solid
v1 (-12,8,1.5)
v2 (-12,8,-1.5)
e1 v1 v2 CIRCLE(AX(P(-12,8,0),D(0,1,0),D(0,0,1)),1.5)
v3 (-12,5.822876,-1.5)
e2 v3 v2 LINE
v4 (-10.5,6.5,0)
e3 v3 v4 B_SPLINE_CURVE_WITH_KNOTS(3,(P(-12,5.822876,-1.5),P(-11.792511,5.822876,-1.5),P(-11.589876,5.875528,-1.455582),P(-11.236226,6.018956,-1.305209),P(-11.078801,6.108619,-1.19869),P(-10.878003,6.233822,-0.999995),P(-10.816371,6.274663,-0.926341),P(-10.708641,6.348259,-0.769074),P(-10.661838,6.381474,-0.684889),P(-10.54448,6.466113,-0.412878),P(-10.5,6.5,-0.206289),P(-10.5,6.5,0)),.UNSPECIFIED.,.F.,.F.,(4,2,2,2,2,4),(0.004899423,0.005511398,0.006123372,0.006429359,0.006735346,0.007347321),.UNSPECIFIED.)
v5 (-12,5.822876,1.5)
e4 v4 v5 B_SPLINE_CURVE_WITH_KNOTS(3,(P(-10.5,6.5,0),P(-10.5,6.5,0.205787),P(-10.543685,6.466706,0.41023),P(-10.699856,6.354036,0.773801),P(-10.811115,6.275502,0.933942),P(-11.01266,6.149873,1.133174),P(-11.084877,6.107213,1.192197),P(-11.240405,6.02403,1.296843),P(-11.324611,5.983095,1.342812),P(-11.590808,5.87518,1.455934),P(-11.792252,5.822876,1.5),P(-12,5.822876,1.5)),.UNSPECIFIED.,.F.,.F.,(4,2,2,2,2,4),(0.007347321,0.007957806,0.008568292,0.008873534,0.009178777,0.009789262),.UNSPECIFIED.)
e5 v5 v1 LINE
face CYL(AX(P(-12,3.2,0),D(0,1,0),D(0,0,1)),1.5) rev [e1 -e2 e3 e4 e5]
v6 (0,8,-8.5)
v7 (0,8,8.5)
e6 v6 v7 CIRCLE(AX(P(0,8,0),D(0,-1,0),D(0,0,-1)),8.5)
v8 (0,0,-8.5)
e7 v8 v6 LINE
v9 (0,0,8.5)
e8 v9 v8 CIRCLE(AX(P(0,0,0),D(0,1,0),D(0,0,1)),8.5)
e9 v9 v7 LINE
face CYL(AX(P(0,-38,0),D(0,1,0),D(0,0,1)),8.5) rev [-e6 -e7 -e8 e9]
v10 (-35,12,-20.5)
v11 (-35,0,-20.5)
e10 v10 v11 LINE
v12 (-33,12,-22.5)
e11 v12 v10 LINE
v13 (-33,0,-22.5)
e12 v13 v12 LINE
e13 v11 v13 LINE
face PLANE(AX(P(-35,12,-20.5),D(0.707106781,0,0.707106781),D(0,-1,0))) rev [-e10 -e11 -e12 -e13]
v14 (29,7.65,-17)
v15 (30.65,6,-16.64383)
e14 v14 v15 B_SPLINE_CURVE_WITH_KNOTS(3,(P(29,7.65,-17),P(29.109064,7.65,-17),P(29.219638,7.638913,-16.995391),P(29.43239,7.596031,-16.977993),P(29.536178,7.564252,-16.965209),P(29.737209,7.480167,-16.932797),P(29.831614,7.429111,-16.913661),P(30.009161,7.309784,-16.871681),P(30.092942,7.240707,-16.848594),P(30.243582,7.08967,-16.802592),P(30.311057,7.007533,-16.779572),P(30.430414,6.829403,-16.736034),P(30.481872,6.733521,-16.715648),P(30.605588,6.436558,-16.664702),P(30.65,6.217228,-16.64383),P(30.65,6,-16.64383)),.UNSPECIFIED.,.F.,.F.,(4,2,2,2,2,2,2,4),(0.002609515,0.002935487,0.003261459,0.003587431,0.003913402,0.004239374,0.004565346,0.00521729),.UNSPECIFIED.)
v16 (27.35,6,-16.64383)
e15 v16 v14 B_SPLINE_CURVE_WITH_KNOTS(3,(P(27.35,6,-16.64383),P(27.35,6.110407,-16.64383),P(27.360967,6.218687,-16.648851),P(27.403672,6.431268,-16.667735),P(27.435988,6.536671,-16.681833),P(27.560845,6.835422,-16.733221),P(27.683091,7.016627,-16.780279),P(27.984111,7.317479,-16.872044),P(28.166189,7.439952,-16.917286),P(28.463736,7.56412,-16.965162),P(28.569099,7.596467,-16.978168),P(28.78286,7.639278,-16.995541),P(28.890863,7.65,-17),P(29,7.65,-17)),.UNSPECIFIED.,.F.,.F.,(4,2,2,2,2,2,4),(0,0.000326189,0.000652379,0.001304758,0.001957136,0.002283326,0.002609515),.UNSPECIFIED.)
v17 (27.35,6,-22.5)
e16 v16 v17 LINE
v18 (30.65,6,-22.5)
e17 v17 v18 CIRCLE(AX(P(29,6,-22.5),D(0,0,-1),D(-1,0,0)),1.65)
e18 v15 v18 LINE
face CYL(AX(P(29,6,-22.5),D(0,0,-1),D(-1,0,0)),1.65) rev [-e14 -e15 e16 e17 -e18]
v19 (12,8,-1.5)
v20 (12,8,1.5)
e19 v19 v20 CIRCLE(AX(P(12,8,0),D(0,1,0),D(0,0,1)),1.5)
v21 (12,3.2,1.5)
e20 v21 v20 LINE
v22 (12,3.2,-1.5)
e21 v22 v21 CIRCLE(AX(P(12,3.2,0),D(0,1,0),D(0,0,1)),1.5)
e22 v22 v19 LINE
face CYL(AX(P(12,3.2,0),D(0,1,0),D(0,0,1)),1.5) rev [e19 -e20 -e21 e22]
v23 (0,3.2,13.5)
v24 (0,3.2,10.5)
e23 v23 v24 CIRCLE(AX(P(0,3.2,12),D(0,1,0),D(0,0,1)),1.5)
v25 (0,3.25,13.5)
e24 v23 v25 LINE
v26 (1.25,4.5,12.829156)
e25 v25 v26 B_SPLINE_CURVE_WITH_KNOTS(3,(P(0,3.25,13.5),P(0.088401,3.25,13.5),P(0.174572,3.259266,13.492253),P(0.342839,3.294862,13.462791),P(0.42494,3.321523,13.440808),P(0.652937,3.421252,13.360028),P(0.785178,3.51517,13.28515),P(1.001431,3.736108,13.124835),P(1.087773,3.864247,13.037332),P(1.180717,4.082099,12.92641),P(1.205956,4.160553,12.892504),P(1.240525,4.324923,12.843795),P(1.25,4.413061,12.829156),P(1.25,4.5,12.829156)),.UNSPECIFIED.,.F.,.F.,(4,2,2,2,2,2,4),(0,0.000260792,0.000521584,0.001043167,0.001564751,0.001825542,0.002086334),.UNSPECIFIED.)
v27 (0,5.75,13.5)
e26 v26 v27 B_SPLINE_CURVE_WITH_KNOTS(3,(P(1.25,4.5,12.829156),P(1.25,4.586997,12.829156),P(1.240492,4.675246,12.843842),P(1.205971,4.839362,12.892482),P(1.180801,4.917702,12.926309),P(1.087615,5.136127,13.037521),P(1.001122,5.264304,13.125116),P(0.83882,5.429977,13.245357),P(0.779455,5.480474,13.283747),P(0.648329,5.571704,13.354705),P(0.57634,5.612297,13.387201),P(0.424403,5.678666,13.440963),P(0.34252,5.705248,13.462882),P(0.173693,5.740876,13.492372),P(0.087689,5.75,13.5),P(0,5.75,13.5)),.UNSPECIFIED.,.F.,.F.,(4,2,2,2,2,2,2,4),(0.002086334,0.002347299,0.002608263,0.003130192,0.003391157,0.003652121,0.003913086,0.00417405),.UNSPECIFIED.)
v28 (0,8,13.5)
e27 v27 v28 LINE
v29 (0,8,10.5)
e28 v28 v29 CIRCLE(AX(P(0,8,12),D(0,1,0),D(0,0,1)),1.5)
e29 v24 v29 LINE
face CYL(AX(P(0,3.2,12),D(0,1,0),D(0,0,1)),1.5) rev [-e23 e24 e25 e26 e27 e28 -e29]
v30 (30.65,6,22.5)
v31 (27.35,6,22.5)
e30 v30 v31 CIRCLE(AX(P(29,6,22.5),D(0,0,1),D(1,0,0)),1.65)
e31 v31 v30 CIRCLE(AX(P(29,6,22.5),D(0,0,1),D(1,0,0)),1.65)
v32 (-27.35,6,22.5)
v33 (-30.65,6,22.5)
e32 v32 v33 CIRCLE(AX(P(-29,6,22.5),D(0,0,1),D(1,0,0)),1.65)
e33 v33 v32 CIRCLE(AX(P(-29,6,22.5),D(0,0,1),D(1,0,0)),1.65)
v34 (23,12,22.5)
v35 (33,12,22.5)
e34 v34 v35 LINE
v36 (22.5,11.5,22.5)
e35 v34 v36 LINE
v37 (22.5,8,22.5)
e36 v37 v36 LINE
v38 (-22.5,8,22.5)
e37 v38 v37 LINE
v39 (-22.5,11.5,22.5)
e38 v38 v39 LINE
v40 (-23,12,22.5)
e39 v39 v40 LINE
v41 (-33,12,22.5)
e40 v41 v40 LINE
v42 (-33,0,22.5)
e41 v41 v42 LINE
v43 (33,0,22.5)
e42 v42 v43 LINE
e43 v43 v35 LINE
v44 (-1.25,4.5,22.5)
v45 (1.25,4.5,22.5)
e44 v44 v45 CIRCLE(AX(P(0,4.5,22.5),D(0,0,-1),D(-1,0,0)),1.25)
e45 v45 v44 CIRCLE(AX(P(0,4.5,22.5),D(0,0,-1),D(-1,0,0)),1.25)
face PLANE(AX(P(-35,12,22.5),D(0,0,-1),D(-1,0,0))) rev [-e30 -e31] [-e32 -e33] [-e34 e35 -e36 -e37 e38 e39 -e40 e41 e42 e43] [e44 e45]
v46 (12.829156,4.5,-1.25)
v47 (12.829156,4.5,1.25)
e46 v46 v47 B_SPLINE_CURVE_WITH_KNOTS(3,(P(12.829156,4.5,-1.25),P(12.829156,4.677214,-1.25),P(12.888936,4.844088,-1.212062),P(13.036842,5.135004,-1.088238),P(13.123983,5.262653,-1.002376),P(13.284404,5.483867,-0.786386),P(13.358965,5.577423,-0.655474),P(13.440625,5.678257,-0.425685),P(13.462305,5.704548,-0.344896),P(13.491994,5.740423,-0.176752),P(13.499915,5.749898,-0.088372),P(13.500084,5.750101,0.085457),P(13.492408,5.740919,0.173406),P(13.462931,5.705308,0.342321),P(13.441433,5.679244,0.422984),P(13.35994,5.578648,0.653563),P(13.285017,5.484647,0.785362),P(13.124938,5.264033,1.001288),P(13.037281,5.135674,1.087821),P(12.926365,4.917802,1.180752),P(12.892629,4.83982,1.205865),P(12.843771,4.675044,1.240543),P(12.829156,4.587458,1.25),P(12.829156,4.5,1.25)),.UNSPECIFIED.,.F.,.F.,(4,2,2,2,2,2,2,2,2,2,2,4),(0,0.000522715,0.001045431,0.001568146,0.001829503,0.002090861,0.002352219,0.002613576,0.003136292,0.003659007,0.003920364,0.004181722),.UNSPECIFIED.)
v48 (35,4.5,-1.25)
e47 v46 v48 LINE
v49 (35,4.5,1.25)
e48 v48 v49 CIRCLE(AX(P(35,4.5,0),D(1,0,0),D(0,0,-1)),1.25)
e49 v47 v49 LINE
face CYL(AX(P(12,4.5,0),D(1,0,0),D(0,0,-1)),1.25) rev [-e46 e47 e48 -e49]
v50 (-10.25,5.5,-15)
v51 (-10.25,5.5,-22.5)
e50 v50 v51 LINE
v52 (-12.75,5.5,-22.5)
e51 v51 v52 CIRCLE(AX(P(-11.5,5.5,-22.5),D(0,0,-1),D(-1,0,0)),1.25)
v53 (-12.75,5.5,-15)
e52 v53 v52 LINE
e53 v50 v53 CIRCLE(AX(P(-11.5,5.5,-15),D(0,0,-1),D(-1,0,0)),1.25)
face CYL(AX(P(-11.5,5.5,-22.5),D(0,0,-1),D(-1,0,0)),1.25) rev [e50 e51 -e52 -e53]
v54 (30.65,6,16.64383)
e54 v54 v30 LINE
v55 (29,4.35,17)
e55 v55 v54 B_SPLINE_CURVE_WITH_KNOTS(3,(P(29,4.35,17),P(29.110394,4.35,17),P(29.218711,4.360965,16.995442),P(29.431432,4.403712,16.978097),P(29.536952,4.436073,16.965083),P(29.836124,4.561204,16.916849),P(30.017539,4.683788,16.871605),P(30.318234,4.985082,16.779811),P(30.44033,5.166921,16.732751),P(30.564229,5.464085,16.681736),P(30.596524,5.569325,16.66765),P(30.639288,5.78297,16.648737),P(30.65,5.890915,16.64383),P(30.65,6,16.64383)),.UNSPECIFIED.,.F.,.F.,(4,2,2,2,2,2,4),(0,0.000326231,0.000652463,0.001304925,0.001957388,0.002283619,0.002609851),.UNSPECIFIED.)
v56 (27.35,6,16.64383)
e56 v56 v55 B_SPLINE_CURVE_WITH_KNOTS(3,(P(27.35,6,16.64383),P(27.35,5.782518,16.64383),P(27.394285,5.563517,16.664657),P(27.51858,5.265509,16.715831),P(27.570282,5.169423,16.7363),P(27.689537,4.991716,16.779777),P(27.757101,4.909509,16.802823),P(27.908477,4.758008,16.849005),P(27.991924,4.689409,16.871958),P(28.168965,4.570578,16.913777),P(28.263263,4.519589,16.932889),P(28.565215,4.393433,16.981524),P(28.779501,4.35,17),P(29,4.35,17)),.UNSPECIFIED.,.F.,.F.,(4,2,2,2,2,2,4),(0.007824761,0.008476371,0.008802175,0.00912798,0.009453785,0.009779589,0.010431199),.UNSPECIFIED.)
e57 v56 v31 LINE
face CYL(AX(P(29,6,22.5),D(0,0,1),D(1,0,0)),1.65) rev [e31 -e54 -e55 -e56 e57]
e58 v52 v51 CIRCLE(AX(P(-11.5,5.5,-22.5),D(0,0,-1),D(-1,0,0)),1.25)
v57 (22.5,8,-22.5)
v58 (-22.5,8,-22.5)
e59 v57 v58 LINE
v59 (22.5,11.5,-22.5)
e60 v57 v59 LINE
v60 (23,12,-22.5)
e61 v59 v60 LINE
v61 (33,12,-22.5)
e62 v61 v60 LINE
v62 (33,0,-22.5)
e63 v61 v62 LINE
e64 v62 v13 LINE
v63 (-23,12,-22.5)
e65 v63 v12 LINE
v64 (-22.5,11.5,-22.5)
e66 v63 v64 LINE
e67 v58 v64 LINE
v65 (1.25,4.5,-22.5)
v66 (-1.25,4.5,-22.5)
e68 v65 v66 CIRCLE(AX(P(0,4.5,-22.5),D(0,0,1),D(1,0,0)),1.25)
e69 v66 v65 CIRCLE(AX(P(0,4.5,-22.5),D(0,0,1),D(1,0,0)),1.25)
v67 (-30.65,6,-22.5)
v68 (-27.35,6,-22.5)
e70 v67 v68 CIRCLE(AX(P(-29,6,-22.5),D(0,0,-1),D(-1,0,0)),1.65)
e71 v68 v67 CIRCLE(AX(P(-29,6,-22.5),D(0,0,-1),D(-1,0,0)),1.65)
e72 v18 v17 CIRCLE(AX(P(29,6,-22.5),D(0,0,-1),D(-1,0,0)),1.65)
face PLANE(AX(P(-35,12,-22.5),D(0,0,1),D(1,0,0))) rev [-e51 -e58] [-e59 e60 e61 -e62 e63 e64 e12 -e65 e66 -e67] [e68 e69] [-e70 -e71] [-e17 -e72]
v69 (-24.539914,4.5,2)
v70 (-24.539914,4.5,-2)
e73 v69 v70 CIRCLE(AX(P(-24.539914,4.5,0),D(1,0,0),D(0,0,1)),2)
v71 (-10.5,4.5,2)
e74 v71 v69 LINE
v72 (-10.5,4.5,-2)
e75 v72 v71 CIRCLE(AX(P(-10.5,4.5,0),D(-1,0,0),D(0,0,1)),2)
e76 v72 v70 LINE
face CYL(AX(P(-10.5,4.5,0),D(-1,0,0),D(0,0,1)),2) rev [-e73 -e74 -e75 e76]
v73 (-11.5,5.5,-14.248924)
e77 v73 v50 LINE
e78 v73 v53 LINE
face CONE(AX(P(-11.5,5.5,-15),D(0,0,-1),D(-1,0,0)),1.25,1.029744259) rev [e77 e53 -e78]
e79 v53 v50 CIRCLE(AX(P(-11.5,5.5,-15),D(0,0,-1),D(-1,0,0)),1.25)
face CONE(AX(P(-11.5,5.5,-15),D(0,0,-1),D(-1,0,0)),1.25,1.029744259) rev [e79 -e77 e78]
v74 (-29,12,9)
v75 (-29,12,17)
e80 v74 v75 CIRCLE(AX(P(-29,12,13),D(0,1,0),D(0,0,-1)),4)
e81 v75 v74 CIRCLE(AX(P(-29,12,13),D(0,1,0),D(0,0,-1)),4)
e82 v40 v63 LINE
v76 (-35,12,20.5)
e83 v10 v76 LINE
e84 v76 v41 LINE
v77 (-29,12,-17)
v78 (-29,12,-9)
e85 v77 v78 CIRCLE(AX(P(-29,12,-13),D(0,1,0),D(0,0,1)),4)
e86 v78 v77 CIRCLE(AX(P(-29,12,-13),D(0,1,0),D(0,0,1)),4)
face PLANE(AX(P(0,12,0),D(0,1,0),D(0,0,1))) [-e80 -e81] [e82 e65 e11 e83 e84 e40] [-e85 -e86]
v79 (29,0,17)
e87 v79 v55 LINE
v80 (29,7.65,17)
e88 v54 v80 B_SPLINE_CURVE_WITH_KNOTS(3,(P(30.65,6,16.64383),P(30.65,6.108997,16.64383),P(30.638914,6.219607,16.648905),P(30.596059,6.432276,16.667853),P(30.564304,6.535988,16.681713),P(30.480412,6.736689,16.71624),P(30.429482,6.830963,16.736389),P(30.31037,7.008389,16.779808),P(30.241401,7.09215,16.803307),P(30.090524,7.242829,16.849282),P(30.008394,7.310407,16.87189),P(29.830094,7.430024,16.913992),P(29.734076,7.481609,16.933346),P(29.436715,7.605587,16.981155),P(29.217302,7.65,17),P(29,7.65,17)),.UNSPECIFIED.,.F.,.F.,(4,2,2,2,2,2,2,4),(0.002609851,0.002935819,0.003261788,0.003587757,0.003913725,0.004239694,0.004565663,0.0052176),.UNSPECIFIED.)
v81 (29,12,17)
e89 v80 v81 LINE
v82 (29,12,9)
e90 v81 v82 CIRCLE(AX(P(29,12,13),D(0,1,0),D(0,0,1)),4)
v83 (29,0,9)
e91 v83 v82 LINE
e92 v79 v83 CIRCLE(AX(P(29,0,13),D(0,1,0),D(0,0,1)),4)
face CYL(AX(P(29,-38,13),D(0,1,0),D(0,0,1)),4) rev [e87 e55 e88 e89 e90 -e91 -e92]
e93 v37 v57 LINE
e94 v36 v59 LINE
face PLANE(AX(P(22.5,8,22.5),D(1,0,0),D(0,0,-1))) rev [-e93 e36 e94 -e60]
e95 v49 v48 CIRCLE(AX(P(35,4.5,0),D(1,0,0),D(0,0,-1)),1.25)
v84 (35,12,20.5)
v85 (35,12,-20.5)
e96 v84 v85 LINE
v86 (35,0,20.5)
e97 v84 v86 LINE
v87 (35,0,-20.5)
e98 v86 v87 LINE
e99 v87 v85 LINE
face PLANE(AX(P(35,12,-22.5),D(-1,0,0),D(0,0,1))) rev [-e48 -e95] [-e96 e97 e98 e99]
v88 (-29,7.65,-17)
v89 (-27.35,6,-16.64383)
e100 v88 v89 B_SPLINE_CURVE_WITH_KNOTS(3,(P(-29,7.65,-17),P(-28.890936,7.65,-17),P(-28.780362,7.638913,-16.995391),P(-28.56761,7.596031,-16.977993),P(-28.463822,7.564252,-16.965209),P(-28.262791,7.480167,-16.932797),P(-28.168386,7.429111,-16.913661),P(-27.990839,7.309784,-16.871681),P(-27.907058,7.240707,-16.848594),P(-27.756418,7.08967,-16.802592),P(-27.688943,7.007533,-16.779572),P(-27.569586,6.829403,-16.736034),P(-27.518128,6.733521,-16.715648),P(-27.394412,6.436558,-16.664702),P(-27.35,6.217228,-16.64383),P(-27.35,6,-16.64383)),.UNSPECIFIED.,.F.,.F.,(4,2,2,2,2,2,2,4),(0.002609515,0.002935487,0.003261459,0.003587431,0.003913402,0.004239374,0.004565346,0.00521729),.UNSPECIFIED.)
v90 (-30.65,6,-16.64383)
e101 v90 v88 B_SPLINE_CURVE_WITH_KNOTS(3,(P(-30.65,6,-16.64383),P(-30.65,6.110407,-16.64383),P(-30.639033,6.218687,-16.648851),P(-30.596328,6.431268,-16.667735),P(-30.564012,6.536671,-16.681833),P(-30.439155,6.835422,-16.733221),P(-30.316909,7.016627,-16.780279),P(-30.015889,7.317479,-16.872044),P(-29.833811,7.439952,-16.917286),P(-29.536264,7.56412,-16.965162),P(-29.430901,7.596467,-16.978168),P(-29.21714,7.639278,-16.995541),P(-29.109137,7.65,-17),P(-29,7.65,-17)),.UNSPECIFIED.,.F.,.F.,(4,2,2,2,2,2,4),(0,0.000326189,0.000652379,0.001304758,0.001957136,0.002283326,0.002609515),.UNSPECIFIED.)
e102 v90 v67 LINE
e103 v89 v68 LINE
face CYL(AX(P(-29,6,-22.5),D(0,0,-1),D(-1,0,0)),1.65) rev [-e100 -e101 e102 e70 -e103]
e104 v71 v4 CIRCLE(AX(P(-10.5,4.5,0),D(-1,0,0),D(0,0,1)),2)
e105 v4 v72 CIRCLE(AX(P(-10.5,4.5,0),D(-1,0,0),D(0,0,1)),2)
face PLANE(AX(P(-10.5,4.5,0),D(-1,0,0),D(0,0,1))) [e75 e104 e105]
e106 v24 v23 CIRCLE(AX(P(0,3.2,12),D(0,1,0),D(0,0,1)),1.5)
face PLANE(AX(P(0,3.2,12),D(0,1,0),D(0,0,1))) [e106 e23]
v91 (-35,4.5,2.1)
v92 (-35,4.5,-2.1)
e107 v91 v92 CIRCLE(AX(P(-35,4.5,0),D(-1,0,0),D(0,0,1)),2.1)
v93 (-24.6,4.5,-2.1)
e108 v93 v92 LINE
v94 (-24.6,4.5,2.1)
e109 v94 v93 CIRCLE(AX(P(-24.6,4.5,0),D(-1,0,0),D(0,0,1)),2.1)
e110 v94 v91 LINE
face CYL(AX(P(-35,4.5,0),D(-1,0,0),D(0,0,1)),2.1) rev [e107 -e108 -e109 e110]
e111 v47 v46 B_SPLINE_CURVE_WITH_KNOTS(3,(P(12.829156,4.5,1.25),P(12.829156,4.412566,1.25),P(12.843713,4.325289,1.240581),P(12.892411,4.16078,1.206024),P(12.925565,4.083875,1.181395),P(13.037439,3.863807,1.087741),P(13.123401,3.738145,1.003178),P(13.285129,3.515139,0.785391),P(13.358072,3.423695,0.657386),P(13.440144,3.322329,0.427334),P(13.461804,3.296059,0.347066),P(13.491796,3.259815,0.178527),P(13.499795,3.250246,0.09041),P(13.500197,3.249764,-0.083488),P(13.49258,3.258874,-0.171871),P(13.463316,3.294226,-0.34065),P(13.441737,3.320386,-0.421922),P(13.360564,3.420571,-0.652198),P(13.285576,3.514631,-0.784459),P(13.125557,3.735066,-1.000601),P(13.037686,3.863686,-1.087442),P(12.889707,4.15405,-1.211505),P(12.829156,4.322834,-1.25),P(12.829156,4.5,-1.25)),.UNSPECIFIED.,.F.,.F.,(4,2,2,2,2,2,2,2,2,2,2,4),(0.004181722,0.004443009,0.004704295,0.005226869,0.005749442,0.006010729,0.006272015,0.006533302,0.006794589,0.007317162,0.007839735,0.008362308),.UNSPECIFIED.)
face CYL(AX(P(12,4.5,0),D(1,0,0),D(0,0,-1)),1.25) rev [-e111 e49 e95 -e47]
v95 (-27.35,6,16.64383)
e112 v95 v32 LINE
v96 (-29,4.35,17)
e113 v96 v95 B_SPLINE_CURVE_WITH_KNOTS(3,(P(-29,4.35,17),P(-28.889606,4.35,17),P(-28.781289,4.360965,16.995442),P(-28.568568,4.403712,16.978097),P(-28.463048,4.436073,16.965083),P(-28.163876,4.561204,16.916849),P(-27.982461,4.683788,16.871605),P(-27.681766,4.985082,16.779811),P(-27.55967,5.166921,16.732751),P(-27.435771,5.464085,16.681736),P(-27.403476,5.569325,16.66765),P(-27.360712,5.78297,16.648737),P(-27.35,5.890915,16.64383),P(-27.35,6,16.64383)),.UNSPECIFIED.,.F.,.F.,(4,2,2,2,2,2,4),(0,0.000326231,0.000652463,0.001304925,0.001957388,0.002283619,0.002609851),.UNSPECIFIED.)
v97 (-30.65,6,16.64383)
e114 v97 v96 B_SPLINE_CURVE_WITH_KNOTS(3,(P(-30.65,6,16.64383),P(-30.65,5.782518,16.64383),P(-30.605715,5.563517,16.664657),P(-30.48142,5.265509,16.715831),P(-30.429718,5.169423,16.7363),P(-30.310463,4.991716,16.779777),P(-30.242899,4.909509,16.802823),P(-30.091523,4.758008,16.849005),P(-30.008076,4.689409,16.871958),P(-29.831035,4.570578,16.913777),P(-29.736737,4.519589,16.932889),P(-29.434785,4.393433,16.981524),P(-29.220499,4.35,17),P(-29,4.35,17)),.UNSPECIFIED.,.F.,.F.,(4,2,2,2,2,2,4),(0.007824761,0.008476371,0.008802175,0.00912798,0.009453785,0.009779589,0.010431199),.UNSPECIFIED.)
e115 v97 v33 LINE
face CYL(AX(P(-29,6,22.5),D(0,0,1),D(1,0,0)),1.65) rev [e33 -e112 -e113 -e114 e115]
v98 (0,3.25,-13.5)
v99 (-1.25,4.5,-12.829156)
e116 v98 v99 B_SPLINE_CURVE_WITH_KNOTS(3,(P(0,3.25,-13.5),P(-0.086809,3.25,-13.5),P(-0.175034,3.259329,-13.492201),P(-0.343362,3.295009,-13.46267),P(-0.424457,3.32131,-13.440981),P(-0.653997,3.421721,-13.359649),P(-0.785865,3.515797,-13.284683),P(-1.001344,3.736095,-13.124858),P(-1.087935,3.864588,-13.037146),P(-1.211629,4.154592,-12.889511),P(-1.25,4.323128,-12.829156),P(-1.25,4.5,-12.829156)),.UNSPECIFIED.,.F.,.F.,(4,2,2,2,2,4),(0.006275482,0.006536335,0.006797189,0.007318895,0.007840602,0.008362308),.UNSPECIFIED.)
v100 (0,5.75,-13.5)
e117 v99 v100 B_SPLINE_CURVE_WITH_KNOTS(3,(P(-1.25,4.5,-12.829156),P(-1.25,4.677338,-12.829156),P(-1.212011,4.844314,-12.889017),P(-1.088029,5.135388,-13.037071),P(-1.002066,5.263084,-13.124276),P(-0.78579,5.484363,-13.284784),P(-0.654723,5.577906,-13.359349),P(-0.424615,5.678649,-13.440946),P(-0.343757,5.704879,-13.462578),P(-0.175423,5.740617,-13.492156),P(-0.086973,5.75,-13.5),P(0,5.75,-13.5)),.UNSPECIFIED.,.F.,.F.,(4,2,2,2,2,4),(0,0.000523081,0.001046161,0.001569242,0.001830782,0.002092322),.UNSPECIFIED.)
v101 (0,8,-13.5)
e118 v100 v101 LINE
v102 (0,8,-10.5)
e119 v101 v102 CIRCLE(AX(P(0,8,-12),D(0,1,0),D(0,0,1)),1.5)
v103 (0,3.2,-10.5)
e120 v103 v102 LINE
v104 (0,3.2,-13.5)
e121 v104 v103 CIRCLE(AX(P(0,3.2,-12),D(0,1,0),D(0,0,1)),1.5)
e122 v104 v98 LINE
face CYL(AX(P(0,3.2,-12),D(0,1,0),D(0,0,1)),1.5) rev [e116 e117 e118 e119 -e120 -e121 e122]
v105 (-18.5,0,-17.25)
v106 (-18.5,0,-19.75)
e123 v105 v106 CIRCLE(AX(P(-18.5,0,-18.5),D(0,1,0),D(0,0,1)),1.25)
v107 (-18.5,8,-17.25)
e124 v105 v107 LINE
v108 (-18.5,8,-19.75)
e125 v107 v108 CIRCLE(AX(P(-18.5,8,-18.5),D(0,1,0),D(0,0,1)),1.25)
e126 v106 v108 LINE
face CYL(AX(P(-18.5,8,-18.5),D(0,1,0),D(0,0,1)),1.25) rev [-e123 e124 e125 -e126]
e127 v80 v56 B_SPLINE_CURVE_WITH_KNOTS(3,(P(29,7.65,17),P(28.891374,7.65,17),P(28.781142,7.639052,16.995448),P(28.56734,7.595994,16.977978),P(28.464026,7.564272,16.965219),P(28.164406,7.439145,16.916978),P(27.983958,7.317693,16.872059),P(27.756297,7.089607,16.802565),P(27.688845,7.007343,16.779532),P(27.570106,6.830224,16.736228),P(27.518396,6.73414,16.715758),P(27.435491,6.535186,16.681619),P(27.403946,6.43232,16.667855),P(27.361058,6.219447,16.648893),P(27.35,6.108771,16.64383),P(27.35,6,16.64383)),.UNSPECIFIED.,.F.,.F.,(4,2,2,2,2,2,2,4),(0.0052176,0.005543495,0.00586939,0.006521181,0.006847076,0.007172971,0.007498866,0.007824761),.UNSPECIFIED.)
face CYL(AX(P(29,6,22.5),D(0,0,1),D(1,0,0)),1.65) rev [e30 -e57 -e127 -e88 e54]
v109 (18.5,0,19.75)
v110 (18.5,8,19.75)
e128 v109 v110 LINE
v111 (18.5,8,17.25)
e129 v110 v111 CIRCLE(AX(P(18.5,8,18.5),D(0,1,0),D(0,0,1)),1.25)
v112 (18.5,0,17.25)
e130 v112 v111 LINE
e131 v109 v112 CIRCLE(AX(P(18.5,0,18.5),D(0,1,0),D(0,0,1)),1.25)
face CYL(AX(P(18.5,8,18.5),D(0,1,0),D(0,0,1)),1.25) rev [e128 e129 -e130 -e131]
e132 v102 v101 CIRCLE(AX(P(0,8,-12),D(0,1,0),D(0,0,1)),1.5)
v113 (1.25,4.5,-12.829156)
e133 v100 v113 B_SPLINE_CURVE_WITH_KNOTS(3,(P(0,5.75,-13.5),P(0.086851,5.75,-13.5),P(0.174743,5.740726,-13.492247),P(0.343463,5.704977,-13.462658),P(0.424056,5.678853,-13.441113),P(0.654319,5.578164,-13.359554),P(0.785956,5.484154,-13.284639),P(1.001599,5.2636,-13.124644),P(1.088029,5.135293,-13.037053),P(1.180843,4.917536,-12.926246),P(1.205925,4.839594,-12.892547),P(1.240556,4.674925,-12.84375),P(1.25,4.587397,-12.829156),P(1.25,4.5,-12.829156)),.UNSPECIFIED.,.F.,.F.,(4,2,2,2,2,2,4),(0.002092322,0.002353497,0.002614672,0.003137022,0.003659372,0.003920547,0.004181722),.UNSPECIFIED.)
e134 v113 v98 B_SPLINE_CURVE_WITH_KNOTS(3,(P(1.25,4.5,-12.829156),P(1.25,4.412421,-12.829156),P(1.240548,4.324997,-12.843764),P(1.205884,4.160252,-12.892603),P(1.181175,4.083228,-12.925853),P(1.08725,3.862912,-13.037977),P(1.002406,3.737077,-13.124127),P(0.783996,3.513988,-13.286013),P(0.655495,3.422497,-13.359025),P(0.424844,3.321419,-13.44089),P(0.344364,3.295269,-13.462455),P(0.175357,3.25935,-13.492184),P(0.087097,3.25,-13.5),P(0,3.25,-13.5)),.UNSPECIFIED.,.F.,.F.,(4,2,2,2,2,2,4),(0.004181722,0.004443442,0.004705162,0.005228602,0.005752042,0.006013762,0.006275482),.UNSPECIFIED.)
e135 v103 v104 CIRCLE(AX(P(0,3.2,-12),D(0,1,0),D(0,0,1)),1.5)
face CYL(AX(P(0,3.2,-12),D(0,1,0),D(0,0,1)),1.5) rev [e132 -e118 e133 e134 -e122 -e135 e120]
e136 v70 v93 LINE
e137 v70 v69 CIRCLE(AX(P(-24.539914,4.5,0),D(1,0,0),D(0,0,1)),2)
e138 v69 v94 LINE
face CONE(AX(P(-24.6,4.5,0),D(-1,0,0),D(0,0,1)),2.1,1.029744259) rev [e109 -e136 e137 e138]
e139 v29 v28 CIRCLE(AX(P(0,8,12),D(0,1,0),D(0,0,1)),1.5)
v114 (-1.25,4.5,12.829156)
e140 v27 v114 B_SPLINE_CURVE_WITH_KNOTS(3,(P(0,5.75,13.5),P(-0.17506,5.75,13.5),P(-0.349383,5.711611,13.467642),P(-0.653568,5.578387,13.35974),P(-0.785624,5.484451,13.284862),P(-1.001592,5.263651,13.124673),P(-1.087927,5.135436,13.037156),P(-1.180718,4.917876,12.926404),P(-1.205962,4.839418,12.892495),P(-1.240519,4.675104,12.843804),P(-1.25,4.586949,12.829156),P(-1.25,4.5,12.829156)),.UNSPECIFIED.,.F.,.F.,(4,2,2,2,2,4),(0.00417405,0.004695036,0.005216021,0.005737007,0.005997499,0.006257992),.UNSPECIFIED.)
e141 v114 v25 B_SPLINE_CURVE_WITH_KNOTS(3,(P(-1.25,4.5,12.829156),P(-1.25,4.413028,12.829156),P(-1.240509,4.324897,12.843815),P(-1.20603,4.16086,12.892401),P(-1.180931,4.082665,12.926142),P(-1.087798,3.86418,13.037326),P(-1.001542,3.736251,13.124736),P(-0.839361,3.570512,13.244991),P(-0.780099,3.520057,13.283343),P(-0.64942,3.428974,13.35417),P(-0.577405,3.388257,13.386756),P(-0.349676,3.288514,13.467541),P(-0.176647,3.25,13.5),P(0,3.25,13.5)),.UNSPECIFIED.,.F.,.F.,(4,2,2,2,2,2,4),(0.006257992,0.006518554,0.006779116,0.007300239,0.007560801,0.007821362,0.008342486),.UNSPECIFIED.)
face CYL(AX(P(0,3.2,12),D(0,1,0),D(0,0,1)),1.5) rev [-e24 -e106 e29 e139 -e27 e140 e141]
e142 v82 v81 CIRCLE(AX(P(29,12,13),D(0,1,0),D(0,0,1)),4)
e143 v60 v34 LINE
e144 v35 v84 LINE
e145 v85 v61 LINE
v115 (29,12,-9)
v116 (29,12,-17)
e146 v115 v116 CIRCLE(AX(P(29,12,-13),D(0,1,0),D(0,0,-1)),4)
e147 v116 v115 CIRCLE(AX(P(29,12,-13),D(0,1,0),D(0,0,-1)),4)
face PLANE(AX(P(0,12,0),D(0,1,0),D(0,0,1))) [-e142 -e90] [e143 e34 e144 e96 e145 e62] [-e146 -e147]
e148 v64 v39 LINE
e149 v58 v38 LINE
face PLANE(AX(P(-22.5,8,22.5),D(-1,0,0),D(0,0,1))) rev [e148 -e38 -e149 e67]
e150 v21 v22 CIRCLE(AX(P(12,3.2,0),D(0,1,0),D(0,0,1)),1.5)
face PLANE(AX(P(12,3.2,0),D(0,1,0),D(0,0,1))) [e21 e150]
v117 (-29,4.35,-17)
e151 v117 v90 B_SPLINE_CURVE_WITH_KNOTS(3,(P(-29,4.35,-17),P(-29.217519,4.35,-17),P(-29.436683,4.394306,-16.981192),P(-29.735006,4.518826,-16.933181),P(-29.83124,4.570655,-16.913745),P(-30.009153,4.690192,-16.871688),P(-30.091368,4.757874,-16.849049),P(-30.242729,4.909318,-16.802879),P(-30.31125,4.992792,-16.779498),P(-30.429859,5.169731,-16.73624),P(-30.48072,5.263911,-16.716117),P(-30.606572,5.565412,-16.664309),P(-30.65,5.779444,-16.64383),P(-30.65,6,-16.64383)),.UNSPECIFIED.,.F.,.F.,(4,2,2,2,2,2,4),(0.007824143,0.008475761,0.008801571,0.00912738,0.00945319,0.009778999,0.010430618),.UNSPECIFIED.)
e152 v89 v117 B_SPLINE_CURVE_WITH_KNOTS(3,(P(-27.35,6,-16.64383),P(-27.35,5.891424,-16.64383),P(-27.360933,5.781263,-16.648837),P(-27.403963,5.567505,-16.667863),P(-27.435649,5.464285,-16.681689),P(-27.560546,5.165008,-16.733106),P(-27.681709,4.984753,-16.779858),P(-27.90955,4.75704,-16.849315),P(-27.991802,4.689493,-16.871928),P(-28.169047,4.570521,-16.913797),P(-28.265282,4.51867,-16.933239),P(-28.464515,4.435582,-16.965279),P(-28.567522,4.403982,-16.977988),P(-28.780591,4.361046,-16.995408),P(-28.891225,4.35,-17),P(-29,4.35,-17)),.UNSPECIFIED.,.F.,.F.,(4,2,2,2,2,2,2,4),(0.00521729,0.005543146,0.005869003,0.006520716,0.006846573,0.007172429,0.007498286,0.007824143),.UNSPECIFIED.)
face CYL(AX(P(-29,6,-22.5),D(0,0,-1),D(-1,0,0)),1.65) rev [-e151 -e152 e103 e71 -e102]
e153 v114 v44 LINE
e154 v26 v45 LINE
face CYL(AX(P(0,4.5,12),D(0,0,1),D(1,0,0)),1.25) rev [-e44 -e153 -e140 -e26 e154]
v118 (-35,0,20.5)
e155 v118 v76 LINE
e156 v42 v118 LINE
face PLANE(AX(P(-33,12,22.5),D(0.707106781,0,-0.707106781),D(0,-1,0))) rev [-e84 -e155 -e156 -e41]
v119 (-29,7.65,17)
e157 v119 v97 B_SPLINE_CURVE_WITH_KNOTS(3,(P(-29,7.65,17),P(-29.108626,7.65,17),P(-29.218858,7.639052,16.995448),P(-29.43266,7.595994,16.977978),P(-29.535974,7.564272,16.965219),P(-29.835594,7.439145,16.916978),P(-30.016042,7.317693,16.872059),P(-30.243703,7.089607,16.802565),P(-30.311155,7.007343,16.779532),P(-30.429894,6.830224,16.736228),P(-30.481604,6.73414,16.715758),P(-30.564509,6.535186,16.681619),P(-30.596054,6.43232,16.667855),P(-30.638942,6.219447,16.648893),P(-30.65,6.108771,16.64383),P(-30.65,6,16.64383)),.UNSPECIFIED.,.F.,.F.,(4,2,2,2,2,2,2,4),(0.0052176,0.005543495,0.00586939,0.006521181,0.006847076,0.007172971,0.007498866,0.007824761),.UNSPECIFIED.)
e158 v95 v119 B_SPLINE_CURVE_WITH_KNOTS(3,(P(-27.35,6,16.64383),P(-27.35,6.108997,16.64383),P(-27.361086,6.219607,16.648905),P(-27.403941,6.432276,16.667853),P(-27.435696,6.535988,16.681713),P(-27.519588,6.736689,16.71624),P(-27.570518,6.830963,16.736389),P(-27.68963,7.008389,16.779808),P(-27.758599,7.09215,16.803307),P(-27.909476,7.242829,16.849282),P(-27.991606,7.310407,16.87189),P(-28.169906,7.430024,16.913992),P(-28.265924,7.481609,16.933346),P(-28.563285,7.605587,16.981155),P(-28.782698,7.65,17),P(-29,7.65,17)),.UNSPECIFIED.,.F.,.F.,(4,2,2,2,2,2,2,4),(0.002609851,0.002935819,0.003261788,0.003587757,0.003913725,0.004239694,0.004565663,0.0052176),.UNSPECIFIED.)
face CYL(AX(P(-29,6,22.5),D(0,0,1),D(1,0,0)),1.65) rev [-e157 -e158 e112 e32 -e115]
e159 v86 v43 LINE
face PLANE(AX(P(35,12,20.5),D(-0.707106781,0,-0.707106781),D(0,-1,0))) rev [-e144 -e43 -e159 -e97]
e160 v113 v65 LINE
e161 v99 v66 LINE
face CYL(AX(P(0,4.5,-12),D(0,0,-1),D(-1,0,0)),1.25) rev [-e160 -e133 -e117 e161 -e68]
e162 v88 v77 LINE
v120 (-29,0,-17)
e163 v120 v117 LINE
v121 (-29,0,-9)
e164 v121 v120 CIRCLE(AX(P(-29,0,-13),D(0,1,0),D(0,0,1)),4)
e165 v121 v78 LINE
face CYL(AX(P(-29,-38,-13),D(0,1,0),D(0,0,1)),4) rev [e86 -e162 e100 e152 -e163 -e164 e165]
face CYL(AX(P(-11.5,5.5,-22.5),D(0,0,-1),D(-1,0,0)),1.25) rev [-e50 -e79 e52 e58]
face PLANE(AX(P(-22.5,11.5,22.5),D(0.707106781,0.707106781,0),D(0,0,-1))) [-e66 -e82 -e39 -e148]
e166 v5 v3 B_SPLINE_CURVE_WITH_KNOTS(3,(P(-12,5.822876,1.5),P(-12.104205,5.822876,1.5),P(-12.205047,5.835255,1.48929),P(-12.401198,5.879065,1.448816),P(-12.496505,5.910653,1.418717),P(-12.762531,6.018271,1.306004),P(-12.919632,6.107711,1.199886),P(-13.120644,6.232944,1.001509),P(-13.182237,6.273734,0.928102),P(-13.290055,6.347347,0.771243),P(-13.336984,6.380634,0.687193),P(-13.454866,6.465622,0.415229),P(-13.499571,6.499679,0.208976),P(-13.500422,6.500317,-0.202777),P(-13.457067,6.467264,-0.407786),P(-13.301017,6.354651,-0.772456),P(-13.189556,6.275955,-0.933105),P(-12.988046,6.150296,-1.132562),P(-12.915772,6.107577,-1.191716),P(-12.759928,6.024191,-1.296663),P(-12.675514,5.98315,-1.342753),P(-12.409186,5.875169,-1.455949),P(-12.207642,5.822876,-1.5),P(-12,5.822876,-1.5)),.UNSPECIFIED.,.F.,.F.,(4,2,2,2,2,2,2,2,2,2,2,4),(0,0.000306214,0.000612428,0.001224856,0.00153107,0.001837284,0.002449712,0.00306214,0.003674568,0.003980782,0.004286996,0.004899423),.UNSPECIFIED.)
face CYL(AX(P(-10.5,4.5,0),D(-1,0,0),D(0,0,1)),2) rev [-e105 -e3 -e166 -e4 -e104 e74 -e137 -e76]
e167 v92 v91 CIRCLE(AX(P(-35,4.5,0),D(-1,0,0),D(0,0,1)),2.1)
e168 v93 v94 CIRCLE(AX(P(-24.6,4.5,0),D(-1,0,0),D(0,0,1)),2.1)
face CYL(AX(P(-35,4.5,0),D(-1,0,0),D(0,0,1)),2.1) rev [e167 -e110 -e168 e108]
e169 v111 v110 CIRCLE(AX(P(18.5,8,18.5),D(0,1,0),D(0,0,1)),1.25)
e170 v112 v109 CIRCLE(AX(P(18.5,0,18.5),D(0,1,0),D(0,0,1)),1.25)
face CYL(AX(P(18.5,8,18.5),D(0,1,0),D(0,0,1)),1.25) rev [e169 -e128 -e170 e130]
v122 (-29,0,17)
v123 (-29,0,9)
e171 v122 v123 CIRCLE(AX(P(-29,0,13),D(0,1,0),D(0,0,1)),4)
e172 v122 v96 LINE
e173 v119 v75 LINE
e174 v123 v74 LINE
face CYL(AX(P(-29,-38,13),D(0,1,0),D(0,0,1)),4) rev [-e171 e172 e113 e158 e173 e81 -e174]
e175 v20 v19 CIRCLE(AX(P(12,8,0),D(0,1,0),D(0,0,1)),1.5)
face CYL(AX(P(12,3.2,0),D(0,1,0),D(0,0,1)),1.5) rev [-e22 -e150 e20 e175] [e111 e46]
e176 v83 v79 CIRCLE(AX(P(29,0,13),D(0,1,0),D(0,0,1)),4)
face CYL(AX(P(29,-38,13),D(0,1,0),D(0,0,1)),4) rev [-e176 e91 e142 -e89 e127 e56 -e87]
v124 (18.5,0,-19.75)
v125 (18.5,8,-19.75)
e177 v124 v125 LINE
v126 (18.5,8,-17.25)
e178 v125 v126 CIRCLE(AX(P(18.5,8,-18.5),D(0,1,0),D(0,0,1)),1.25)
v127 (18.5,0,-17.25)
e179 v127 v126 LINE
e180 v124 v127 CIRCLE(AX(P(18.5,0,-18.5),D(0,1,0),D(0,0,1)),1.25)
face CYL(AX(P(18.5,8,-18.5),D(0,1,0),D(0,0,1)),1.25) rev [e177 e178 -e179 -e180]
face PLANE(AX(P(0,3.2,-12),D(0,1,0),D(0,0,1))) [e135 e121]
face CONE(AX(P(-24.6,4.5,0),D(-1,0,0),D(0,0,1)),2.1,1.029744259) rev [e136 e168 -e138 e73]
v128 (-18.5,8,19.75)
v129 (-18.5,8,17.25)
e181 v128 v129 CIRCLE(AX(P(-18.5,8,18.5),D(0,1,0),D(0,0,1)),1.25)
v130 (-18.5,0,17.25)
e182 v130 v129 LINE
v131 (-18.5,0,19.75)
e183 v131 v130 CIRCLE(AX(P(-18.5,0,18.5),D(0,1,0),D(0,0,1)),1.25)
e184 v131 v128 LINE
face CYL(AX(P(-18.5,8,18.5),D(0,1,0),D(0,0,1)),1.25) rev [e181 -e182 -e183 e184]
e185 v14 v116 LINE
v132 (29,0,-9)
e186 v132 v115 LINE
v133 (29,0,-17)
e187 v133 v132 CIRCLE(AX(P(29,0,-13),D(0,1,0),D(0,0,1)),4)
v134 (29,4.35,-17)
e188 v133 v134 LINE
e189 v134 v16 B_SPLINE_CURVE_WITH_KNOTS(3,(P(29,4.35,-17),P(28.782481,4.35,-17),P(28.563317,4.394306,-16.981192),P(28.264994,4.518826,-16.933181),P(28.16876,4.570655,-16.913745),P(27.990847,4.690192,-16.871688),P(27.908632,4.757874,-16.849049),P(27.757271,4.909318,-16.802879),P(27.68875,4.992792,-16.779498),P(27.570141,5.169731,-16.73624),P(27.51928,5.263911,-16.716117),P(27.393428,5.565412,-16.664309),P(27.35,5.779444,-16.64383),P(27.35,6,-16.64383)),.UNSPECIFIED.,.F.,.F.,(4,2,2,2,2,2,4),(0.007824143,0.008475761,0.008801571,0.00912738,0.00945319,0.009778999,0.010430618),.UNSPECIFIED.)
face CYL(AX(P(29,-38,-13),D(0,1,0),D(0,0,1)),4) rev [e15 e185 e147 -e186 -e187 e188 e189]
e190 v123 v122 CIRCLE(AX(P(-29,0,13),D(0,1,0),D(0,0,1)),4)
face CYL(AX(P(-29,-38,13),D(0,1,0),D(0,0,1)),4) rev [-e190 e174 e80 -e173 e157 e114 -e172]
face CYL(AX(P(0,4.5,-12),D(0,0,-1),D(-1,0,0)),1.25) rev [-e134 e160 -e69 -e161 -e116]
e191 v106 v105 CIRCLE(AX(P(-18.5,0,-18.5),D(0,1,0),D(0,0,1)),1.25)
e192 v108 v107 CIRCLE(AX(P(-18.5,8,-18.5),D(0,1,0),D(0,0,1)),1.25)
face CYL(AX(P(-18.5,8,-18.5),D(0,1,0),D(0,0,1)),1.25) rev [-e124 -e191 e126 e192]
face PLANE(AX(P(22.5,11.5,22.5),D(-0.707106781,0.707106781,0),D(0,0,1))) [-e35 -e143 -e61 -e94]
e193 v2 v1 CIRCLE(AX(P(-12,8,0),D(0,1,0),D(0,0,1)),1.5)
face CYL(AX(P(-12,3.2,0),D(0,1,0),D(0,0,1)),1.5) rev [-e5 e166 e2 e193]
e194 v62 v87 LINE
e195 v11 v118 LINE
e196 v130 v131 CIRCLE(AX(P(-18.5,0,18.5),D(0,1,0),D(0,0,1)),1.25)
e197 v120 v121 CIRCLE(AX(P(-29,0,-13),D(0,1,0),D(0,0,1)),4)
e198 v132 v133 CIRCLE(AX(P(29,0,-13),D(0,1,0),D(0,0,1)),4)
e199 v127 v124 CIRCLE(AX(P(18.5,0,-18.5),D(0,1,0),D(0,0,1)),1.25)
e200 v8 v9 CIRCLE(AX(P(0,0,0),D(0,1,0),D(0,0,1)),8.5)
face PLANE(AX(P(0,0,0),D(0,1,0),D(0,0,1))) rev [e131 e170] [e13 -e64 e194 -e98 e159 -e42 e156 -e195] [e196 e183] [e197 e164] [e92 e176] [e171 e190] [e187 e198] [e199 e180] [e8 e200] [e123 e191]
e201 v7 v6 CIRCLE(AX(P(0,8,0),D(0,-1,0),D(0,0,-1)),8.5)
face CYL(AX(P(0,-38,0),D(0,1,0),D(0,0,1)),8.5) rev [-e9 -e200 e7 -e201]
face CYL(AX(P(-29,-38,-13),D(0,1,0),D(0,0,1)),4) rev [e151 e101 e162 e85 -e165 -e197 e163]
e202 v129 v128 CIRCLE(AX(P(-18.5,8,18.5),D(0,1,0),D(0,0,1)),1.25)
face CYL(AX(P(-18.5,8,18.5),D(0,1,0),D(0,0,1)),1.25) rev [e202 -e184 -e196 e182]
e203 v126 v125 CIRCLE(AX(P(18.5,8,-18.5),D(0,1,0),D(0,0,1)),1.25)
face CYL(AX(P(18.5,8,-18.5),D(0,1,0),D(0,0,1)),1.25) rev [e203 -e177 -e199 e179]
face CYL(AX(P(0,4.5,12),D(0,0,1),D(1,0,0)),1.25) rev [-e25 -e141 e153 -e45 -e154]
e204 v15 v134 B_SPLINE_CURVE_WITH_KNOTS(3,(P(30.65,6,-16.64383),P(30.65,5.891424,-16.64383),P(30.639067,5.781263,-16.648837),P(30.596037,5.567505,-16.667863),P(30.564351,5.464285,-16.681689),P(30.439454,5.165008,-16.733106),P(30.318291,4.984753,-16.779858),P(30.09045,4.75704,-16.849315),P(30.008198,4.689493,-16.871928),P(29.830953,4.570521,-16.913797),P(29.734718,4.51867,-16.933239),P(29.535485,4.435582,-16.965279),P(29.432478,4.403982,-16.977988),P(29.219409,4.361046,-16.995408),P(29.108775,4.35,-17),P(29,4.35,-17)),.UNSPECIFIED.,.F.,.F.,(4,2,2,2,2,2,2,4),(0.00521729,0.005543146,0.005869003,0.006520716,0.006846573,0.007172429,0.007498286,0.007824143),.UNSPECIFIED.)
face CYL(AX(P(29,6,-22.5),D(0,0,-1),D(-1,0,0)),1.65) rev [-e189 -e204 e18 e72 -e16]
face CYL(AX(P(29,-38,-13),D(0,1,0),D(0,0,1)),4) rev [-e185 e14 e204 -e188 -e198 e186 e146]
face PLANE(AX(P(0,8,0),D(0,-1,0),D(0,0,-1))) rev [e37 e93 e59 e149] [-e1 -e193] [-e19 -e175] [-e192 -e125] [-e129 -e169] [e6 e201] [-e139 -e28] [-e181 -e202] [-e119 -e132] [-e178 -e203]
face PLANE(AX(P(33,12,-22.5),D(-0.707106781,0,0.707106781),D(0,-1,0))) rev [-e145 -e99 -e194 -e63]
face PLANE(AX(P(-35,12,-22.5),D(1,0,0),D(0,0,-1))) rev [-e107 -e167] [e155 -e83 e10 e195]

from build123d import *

# Parameters (mm, degrees)
SKETCH1_W                       = 70
SKETCH1_H                       = 45
BOSS_EXTRUDE1_DEPTH             = 12
SKETCH2_W                       = 45
SKETCH2_H                       = 45
CUT_EXTRUDE1_DEPTH              = 4
SKETCH3_R                       = 4
CUT_EXTRUDE2_DEPTH              = 50
SKETCH4_R                       = 8.5
CUT_EXTRUDE3_DEPTH              = 50
SKETCH5_R                       = 0.5
CUT_EXTRUDE4_DEPTH              = 7
M4_TAPPED_HOLE1_AT_2_COUNT      = 2
M4_TAPPED_HOLE1_AT_2_PITCH      = 58
SKETCH7_R                       = 1.5
CUT_EXTRUDE5_DEPTH              = 4.8
SKETCH8_R                       = 1.25
CUT_EXTRUDE6_DEPTH              = 23
CIRPATTERN1_COUNT               = 4
M3_TAPPED_HOLE4_D               = 2.5
M3_TAPPED_HOLE4_DEPTH           = 6
M3_TAPPED_HOLE4_TIP             = 0.751075774
M3_TAPPED_HOLE3_D               = 2.5
M3_TAPPED_HOLE3_DEPTH           = 7.5
M3_TAPPED_HOLE3_TIP             = 0.751075774
M3_TAPPED_HOLE3_ON_FACE_2_D     = 2.5
M3_TAPPED_HOLE3_ON_FACE_2_DEPTH = 7.5
M3_TAPPED_HOLE3_ON_FACE_2_TIP   = 0.751075774
CHAMFER1_SIZE                   = 0.5
M5_TAPPED_HOLE1_D               = 4.2
M5_TAPPED_HOLE1_DEPTH           = 10.4
M5_TAPPED_HOLE1_TIP             = 1.2618073
SKETCH13_R                      = 2
CUT_EXTRUDE8_DEPTH              = 24.5
CHAMFER2_SIZE                   = 2
M3_TAPPED_HOLE5_D               = 2.5
M3_TAPPED_HOLE6_D               = 2.5
M3_TAPPED_HOLE6_DEPTH           = 7.5
M3_TAPPED_HOLE6_TIP             = 0.751075774


with BuildPart() as part:
    # Sketch1 → Boss-Extrude1 (new body)
    with BuildSketch(Plane(origin=(0, 0, 0), x_dir=(1, 0, 0), z_dir=(0, 1, 0))):
        Rectangle(SKETCH1_W, SKETCH1_H)
    extrude(amount=BOSS_EXTRUDE1_DEPTH)

    # Sketch2 → Cut-Extrude1 (cut)
    with BuildSketch(Plane(origin=(0, 12, 0), x_dir=(1, 0, 0), z_dir=(0, 1, 0))):
        Rectangle(SKETCH2_W, SKETCH2_H)
    extrude(amount=-CUT_EXTRUDE1_DEPTH, mode=Mode.SUBTRACT)

    # Sketch3 → Cut-Extrude2 (cut)
    with BuildSketch(Plane(origin=(0, 12, 0), x_dir=(1, 0, 0), z_dir=(0, 1, 0))):
        with Locations(Location((-29, 13, 0), (0, 0, 270))):
            Circle(SKETCH3_R)
        with Locations(Location((-29, -13, 0), (0, 0, 270))):
            Circle(SKETCH3_R)
        with Locations(Location((29, -13, 0), (0, 0, 270))):
            Circle(SKETCH3_R)
        with Locations(Location((29, 13, 0), (0, 0, 270))):
            Circle(SKETCH3_R)
    extrude(amount=-CUT_EXTRUDE2_DEPTH, mode=Mode.SUBTRACT)

    # Sketch4 → Cut-Extrude3 (cut)
    with BuildSketch(Plane(origin=(0, 12, 0), x_dir=(1, 0, 0), z_dir=(0, 1, 0))):
        with Locations(Location((0, 0, 0), (0, 0, 270))):
            Circle(SKETCH4_R)
    extrude(amount=-CUT_EXTRUDE3_DEPTH, mode=Mode.SUBTRACT)

    # Sketch5 → Cut-Extrude4 (cut)
    with BuildSketch(Plane.XY.offset(22.5)):
        with Locations((-29, 6)):
            Circle(SKETCH5_R)
        with Locations(Location((29, 6, 0), (0, 0, 270))):
            Circle(SKETCH5_R)
    extrude(amount=-CUT_EXTRUDE4_DEPTH, mode=Mode.SUBTRACT)

    # Sketch6 → M4 Tapped Hole1 (revolve, cut)
    with BuildSketch(Plane(origin=(-29, 6, 22.5), x_dir=(0, -1, 0), z_dir=(1, 0, 0))):
        Polygon((0, 0), (0, 11.091420021), (1.65, 10.1), (1.65, 0), align=None)
    m4_tapped_hole1 = revolve(axis=Axis((-29, 6, 28.85), (0, 0, -1)), mode=Mode.SUBTRACT)

    # M4 Tapped Hole1 at 2: M4 Tapped Hole1 ×2
    with Locations(*[(i * M4_TAPPED_HOLE1_AT_2_PITCH, 0, 0) for i in range(1, M4_TAPPED_HOLE1_AT_2_COUNT)]):
        add(m4_tapped_hole1, mode=Mode.SUBTRACT)

    # Mirror1: M4 Tapped Hole1 across plane
    add(m4_tapped_hole1.mirror(Plane.XY), mode=Mode.SUBTRACT)

    # Mirror1 copy 1 sketch → Mirror1 copy 1 (revolve, cut)
    with BuildSketch(Plane(origin=(29, 6, -22.5), x_dir=(0, -1, 0), z_dir=(1, 0, 0))):
        Polygon((0, 0), (0, -11.091420021), (1.65, -10.1), (1.65, 0), align=None)
    revolve(axis=Axis((29, 6, -28.85), (0, 0, -1)), mode=Mode.SUBTRACT)

    # Sketch7 → Cut-Extrude5 (cut)
    with BuildSketch(Plane(origin=(0, 8, 0), x_dir=(1, 0, 0), z_dir=(0, 1, 0))):
        with Locations(Location((0, 12, 0), (0, 0, 270))):
            Circle(SKETCH7_R)
        with Locations(Location((12, 0, 0), (0, 0, 270))):
            Circle(SKETCH7_R)
        with Locations(Location((0, -12, 0), (0, 0, 270))):
            Circle(SKETCH7_R)
        with Locations(Location((-12, 0, 0), (0, 0, 270))):
            Circle(SKETCH7_R)
    extrude(amount=-CUT_EXTRUDE5_DEPTH, mode=Mode.SUBTRACT)

    # Sketch8 → Cut-Extrude6 (cut)
    with BuildSketch(Plane.ZY.offset(35)):
        with Locations((0, 4.5)):
            Circle(SKETCH8_R)
    cut_extrude6 = extrude(amount=-CUT_EXTRUDE6_DEPTH, mode=Mode.SUBTRACT)

    # CirPattern1: Cut-Extrude6 ×4 about axis
    cirpattern1_axis = Axis((0, -38, 0), (0, 1, 0))
    for i in range(1, CIRPATTERN1_COUNT):
        add(cut_extrude6.rotate(cirpattern1_axis, i * 360 / CIRPATTERN1_COUNT), mode=Mode.SUBTRACT)

    # M3 Tapped Hole4
    with Locations(Plane(origin=(35, 4.5, 0), x_dir=(0, 0, 1), z_dir=(1, 0, 0))):
        with Locations((0, 0)):
            Hole(M3_TAPPED_HOLE4_D / 2, depth=M3_TAPPED_HOLE4_DEPTH)
            with Locations((0, 0, -(M3_TAPPED_HOLE4_DEPTH + M3_TAPPED_HOLE4_TIP / 2))):  # 118° drill point
                Cone(0, M3_TAPPED_HOLE4_D / 2, M3_TAPPED_HOLE4_TIP, mode=Mode.SUBTRACT)

    # M3 Tapped Hole3
    with Locations(Plane(origin=(0, 4.5, 22.5), x_dir=(1, 0, 0), z_dir=(0, 0, 1))):
        with Locations((0, 0)):
            Hole(M3_TAPPED_HOLE3_D / 2, depth=M3_TAPPED_HOLE3_DEPTH)
            with Locations((0, 0, -(M3_TAPPED_HOLE3_DEPTH + M3_TAPPED_HOLE3_TIP / 2))):  # 118° drill point
                Cone(0, M3_TAPPED_HOLE3_D / 2, M3_TAPPED_HOLE3_TIP, mode=Mode.SUBTRACT)

    # M3 Tapped Hole3 on face 2
    with Locations(Plane(origin=(0, 4.5, -22.5), x_dir=(1, 0, 0), z_dir=(0, 0, 1))):
        with Locations((0, 0)):
            Hole(M3_TAPPED_HOLE3_ON_FACE_2_D / 2, depth=M3_TAPPED_HOLE3_ON_FACE_2_DEPTH)
            with Locations((0, 0, -(M3_TAPPED_HOLE3_ON_FACE_2_DEPTH + M3_TAPPED_HOLE3_ON_FACE_2_TIP / 2))):  # 118° drill point
                Cone(0, M3_TAPPED_HOLE3_ON_FACE_2_D / 2, M3_TAPPED_HOLE3_ON_FACE_2_TIP, mode=Mode.SUBTRACT)

    # Chamfer1
    chamfer1_edges = [part.edges().sort_by_distance(p)[0] for p in [
        (22.5, 12, 0),
        (-22.5, 12, 0),
    ]]
    chamfer(chamfer1_edges, length=CHAMFER1_SIZE)

    # M5 Tapped Hole1
    with Locations(Plane(origin=(-35, 4.5, 0), x_dir=(0, 0, -1), z_dir=(-1, 0, 0))):
        with Locations((0, 0)):
            Hole(M5_TAPPED_HOLE1_D / 2, depth=M5_TAPPED_HOLE1_DEPTH)
            with Locations((0, 0, -(M5_TAPPED_HOLE1_DEPTH + M5_TAPPED_HOLE1_TIP / 2))):  # 118° drill point
                Cone(0, M5_TAPPED_HOLE1_D / 2, M5_TAPPED_HOLE1_TIP, mode=Mode.SUBTRACT)

    # Sketch13 → Cut-Extrude8 (cut)
    with BuildSketch(Plane.ZY.offset(35)):
        with Locations((0, 4.5)):
            Circle(SKETCH13_R)
    extrude(amount=-CUT_EXTRUDE8_DEPTH, mode=Mode.SUBTRACT)

    # Chamfer2
    chamfer2_edges = [part.edges().sort_by_distance(p)[0] for p in [
        (35, 6, 22.5),
        (-35, 6, 22.5),
        (-35, 6, -22.5),
        (35, 6, -22.5),
    ]]
    chamfer(chamfer2_edges, length=CHAMFER2_SIZE)

    # M3 Tapped Hole5 (through all)
    with Locations(Plane(origin=(0, 8, 0), x_dir=(1, 0, 0), z_dir=(0, 1, 0))):
        with Locations((18.5, 18.5), (-18.5, 18.5), (-18.5, -18.5), (18.5, -18.5)):
            Hole(M3_TAPPED_HOLE5_D / 2)

    # M3 Tapped Hole6
    with Locations(Plane(origin=(0, 0, -22.5), x_dir=(-1, 0, 0), z_dir=(0, 0, -1))):
        with Locations((11.5, 5.5)):
            Hole(M3_TAPPED_HOLE6_D / 2, depth=M3_TAPPED_HOLE6_DEPTH)
            with Locations((0, 0, -(M3_TAPPED_HOLE6_DEPTH + M3_TAPPED_HOLE6_TIP / 2))):  # 118° drill point
                Cone(0, M3_TAPPED_HOLE6_D / 2, M3_TAPPED_HOLE6_TIP, mode=Mode.SUBTRACT)


solid = part.part
